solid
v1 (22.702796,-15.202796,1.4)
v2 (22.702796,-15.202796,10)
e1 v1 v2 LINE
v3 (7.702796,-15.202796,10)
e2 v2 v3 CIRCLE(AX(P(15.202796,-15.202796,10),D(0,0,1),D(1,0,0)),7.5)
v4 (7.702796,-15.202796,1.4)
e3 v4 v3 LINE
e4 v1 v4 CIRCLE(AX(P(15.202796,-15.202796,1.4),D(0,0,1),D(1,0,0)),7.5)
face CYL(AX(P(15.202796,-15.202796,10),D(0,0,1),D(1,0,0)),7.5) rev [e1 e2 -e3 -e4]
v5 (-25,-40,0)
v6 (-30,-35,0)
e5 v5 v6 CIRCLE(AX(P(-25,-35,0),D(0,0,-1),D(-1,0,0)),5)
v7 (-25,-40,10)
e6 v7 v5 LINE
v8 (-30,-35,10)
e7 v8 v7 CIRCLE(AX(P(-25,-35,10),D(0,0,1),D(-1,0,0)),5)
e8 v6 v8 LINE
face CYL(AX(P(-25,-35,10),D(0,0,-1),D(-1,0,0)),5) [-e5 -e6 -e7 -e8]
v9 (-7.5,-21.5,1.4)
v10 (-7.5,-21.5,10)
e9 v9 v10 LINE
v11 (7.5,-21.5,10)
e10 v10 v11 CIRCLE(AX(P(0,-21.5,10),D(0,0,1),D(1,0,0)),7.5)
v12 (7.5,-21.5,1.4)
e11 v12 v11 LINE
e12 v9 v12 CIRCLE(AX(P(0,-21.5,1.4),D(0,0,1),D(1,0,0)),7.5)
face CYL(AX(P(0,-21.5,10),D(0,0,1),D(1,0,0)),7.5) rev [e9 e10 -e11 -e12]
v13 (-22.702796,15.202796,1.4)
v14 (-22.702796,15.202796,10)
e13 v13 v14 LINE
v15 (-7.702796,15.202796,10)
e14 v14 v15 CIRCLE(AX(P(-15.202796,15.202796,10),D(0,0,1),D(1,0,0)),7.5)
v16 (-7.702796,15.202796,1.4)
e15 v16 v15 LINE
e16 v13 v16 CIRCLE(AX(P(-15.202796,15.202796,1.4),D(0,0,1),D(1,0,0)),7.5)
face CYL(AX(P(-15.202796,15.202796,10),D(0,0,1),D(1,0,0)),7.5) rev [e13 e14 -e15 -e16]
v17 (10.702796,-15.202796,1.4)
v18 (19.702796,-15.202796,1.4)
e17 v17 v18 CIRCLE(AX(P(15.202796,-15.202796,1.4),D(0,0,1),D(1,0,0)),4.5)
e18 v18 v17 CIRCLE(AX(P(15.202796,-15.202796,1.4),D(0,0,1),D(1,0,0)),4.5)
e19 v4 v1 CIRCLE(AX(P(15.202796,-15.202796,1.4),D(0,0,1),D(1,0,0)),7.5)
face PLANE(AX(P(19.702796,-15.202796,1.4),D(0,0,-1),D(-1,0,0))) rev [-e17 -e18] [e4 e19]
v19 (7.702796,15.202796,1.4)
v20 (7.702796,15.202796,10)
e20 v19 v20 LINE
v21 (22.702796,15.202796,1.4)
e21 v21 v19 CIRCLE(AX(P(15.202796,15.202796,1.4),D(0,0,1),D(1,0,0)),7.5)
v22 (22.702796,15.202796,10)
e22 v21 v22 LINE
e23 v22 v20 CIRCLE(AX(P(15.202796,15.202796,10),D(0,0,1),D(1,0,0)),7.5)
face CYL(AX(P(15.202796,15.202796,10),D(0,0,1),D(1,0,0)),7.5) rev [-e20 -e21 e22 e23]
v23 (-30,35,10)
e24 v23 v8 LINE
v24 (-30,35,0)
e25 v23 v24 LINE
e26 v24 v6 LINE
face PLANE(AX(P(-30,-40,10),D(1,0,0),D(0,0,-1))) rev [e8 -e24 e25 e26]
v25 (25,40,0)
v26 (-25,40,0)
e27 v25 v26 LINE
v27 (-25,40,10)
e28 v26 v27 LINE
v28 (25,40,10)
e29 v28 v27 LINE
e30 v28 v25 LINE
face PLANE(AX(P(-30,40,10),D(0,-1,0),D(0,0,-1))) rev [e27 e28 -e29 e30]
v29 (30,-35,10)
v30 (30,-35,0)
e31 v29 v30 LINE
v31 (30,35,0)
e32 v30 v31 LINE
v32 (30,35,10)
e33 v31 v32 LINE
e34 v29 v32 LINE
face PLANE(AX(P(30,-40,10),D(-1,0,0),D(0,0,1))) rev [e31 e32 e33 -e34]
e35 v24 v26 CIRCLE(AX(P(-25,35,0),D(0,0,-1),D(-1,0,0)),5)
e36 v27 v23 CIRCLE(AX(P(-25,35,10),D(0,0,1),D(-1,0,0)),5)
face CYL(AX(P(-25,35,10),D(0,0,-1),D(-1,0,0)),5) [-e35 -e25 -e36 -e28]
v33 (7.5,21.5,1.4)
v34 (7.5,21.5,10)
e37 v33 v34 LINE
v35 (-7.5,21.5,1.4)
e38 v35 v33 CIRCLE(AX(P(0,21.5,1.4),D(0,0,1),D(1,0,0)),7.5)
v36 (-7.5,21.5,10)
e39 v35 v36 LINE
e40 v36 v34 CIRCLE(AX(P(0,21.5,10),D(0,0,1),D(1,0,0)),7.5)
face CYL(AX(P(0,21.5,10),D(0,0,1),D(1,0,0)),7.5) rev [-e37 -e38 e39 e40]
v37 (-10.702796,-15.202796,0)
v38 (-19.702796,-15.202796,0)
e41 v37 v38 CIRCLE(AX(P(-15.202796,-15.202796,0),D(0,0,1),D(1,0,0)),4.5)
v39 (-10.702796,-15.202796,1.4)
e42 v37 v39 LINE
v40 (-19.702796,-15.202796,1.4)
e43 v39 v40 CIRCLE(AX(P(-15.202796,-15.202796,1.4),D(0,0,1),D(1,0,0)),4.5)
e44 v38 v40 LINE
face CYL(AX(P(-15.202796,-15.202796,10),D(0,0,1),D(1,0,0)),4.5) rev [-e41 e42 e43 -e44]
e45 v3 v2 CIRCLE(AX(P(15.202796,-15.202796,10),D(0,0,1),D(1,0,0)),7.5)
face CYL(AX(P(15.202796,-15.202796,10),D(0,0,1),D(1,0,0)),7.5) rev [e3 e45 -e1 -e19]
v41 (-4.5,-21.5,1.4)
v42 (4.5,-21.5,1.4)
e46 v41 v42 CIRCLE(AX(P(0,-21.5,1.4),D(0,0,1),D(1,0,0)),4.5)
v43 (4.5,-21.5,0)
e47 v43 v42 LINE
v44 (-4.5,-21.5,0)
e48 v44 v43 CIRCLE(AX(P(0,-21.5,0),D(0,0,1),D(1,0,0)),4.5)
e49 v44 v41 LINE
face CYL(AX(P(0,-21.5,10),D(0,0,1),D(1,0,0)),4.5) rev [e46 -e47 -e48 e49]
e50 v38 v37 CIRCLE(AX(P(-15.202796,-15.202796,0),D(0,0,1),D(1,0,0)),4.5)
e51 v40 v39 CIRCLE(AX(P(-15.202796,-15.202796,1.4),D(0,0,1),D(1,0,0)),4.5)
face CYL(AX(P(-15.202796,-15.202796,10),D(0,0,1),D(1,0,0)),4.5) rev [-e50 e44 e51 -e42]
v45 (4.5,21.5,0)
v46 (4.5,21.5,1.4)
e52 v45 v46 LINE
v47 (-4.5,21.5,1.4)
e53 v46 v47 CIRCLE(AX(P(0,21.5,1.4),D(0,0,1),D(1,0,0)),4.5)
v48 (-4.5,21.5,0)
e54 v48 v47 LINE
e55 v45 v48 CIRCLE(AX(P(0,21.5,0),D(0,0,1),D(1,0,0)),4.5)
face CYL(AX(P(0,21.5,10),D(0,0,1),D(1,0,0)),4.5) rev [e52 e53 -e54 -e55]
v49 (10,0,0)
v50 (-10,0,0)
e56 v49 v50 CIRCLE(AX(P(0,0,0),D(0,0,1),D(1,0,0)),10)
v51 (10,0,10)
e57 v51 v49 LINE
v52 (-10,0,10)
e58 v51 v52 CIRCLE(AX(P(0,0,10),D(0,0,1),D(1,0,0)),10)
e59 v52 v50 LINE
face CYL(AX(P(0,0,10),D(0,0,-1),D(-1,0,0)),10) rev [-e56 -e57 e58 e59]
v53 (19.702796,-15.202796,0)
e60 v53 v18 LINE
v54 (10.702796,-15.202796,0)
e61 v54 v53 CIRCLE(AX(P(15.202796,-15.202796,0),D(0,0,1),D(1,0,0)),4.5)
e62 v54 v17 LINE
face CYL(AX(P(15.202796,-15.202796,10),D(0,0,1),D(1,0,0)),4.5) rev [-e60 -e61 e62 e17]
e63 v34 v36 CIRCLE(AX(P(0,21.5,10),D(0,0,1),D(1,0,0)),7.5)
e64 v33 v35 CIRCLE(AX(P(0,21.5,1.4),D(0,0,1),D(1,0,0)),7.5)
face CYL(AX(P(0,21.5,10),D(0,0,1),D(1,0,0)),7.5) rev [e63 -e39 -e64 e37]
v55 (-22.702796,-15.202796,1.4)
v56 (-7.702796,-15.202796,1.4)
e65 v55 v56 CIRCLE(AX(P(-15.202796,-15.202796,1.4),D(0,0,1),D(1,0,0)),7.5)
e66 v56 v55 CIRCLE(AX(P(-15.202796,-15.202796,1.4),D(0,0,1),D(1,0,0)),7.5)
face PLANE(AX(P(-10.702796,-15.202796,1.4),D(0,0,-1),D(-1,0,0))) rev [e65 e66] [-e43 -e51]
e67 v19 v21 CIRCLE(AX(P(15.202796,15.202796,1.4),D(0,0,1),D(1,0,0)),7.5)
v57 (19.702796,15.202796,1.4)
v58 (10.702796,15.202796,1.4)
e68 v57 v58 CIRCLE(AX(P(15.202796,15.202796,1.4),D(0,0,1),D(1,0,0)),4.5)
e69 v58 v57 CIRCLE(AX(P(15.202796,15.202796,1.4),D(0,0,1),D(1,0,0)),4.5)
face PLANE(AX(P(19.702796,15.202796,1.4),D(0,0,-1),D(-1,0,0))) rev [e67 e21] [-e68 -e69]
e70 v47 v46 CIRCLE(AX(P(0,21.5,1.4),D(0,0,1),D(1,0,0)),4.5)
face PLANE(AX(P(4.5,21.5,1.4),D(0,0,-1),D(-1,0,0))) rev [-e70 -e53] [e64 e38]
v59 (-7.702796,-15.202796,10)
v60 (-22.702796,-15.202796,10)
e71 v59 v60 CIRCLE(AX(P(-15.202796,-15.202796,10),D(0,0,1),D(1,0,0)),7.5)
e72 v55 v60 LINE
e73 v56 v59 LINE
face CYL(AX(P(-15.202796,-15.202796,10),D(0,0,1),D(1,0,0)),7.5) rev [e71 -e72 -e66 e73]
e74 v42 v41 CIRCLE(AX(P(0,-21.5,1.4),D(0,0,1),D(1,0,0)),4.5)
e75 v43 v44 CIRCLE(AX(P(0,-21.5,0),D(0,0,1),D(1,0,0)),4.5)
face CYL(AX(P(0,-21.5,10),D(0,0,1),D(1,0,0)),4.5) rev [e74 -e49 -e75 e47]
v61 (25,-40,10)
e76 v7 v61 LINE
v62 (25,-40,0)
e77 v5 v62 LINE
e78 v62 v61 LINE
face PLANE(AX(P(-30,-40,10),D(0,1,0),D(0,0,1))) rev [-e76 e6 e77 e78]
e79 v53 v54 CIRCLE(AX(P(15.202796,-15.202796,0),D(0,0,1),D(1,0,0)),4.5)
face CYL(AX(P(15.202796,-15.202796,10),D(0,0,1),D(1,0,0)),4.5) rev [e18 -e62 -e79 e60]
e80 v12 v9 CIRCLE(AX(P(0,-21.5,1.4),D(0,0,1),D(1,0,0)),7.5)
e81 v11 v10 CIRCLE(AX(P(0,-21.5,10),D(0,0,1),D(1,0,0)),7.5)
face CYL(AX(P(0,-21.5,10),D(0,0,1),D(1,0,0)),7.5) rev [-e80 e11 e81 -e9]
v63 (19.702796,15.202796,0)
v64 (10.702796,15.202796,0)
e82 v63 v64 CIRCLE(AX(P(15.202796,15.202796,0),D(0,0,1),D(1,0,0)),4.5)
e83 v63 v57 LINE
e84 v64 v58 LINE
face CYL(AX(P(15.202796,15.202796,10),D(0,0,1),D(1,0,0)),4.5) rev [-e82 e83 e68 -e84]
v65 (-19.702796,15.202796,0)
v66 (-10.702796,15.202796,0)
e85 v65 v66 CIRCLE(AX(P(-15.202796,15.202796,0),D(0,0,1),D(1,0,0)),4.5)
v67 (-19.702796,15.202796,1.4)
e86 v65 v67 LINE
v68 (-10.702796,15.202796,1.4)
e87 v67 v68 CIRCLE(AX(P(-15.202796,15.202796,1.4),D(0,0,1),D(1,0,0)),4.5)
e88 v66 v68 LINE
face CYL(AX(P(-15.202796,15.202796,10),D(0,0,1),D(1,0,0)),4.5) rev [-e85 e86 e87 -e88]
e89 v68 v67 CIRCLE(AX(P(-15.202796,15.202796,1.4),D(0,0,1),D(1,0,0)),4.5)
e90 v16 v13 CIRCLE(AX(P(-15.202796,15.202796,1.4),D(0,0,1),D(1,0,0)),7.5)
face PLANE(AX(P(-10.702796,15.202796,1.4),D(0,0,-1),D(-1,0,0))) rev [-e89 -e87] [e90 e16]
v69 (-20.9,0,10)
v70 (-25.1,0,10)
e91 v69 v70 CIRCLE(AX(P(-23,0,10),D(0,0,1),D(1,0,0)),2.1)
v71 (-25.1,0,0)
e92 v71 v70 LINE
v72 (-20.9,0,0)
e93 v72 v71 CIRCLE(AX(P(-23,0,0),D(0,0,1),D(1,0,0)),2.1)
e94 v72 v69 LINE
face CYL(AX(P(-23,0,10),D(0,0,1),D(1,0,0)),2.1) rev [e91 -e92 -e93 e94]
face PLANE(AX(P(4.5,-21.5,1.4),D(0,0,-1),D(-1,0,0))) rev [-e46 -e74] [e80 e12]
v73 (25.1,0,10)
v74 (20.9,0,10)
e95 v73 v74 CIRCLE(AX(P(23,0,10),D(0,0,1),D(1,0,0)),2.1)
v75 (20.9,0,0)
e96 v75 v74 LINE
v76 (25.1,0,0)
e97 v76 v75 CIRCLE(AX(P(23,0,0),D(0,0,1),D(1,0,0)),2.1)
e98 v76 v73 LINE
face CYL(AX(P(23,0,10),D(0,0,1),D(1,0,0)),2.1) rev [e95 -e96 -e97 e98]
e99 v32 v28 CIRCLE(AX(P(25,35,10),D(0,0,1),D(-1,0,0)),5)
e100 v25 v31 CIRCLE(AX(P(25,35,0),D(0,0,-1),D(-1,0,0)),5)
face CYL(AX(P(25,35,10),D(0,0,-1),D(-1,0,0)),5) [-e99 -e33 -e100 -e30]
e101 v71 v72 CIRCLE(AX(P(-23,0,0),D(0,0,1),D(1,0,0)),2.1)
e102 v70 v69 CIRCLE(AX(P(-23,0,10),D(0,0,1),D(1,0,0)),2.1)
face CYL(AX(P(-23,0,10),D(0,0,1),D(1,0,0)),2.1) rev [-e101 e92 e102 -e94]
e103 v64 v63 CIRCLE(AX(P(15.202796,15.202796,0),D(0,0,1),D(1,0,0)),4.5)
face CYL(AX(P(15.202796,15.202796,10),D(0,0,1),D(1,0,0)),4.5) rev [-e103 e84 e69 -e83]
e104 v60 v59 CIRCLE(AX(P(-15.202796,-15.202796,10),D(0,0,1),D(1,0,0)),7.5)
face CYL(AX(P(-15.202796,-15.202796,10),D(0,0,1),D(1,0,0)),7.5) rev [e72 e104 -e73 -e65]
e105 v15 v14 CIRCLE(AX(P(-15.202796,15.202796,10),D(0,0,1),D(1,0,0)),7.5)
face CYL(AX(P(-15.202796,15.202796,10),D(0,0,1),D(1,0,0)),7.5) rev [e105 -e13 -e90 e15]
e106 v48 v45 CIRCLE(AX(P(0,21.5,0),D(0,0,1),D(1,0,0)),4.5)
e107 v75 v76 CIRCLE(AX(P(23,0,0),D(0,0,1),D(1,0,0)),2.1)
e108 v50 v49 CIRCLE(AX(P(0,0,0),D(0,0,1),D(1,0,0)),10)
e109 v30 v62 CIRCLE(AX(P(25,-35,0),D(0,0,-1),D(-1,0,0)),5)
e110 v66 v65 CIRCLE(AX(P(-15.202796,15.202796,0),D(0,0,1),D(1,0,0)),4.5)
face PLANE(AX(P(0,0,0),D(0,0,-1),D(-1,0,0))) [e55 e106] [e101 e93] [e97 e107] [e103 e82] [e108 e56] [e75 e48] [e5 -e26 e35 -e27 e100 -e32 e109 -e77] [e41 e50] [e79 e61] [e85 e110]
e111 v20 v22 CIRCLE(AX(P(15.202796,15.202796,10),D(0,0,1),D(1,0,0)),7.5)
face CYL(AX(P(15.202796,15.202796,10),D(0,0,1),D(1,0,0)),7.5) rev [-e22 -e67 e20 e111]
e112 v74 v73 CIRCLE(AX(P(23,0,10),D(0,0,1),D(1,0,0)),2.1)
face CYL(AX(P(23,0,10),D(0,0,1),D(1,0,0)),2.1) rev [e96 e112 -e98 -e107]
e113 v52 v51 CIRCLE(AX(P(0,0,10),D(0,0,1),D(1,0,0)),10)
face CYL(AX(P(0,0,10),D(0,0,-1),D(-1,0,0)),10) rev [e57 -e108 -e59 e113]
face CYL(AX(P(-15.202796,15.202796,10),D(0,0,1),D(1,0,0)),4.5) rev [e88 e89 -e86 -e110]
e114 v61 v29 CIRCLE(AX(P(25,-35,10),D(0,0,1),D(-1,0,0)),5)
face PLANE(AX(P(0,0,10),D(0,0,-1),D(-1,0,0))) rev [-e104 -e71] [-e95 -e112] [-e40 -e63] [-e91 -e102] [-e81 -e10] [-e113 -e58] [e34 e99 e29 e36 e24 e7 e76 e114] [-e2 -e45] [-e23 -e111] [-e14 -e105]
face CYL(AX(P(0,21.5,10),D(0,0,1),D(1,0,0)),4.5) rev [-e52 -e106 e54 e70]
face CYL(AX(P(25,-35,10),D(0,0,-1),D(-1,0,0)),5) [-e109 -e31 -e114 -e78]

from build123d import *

# Parameters (mm, degrees)
SKETCH1_W                                           = 60
SKETCH1_H                                           = 80
SKETCH1_R                                           = 10
SKETCH1_R_2                                         = 2
BOSS_EXTRUDE1_DEPTH                                 = 10
M5_TAPPED_HOLE1_D                                   = 4.2
CBORE_FOR_M8_HEX_SOCKET_HEAD_CAP_SCREW1_D           = 9
CBORE_FOR_M8_HEX_SOCKET_HEAD_CAP_SCREW1_CBORE_D     = 15
CBORE_FOR_M8_HEX_SOCKET_HEAD_CAP_SCREW1_CBORE_DEPTH = 8.6
CIRPATTERN1_COUNT                                   = 8
FILLET1_R                                           = 5


with BuildPart() as part:
    # Sketch1 → Boss-Extrude1 (new body)
    with BuildSketch(Plane.XY):
        Rectangle(SKETCH1_W, SKETCH1_H)
        Circle(SKETCH1_R, mode=Mode.SUBTRACT)
        with Locations((-23, 0)):
            Circle(SKETCH1_R_2, mode=Mode.SUBTRACT)
        with Locations(Location((23, 0, 0), (0, 0, 180))):
            Circle(SKETCH1_R_2, mode=Mode.SUBTRACT)
    extrude(amount=BOSS_EXTRUDE1_DEPTH)

    # M5 Tapped Hole1 (through all)
    with Locations(Plane.XY.offset(10)):
        with Locations((-23, 0), (23, 0)):
            Hole(M5_TAPPED_HOLE1_D / 2)

    # CBORE for M8 Hex Socket Head Cap Screw1 (through all)
    with Locations(Plane.XY.offset(10)):
        with Locations((0, 21.5)):
            cbore_for_m8_hex_socket_head_cap_screw1 = CounterBoreHole(CBORE_FOR_M8_HEX_SOCKET_HEAD_CAP_SCREW1_D / 2, CBORE_FOR_M8_HEX_SOCKET_HEAD_CAP_SCREW1_CBORE_D / 2, CBORE_FOR_M8_HEX_SOCKET_HEAD_CAP_SCREW1_CBORE_DEPTH)

    # CirPattern1: CBORE for M8 Hex Socket Head Cap Screw1 ×8 about axis, 2 skipped
    cirpattern1_axis = Axis((0, 0, 0), (0, 0, 1))
    add([cbore_for_m8_hex_socket_head_cap_screw1.rotate(cirpattern1_axis, i * 360 / CIRPATTERN1_COUNT) for i in range(1, CIRPATTERN1_COUNT) if i not in (2, 6)], mode=Mode.SUBTRACT)

    # Fillet1
    fillet1_edges = [part.edges().sort_by_distance(p)[0] for p in [
        (30, -40, 5),
        (-30, -40, 5),
        (-30, 40, 5),
        (30, 40, 5),
    ]]
    fillet(fillet1_edges, radius=FILLET1_R)


solid = part.part
